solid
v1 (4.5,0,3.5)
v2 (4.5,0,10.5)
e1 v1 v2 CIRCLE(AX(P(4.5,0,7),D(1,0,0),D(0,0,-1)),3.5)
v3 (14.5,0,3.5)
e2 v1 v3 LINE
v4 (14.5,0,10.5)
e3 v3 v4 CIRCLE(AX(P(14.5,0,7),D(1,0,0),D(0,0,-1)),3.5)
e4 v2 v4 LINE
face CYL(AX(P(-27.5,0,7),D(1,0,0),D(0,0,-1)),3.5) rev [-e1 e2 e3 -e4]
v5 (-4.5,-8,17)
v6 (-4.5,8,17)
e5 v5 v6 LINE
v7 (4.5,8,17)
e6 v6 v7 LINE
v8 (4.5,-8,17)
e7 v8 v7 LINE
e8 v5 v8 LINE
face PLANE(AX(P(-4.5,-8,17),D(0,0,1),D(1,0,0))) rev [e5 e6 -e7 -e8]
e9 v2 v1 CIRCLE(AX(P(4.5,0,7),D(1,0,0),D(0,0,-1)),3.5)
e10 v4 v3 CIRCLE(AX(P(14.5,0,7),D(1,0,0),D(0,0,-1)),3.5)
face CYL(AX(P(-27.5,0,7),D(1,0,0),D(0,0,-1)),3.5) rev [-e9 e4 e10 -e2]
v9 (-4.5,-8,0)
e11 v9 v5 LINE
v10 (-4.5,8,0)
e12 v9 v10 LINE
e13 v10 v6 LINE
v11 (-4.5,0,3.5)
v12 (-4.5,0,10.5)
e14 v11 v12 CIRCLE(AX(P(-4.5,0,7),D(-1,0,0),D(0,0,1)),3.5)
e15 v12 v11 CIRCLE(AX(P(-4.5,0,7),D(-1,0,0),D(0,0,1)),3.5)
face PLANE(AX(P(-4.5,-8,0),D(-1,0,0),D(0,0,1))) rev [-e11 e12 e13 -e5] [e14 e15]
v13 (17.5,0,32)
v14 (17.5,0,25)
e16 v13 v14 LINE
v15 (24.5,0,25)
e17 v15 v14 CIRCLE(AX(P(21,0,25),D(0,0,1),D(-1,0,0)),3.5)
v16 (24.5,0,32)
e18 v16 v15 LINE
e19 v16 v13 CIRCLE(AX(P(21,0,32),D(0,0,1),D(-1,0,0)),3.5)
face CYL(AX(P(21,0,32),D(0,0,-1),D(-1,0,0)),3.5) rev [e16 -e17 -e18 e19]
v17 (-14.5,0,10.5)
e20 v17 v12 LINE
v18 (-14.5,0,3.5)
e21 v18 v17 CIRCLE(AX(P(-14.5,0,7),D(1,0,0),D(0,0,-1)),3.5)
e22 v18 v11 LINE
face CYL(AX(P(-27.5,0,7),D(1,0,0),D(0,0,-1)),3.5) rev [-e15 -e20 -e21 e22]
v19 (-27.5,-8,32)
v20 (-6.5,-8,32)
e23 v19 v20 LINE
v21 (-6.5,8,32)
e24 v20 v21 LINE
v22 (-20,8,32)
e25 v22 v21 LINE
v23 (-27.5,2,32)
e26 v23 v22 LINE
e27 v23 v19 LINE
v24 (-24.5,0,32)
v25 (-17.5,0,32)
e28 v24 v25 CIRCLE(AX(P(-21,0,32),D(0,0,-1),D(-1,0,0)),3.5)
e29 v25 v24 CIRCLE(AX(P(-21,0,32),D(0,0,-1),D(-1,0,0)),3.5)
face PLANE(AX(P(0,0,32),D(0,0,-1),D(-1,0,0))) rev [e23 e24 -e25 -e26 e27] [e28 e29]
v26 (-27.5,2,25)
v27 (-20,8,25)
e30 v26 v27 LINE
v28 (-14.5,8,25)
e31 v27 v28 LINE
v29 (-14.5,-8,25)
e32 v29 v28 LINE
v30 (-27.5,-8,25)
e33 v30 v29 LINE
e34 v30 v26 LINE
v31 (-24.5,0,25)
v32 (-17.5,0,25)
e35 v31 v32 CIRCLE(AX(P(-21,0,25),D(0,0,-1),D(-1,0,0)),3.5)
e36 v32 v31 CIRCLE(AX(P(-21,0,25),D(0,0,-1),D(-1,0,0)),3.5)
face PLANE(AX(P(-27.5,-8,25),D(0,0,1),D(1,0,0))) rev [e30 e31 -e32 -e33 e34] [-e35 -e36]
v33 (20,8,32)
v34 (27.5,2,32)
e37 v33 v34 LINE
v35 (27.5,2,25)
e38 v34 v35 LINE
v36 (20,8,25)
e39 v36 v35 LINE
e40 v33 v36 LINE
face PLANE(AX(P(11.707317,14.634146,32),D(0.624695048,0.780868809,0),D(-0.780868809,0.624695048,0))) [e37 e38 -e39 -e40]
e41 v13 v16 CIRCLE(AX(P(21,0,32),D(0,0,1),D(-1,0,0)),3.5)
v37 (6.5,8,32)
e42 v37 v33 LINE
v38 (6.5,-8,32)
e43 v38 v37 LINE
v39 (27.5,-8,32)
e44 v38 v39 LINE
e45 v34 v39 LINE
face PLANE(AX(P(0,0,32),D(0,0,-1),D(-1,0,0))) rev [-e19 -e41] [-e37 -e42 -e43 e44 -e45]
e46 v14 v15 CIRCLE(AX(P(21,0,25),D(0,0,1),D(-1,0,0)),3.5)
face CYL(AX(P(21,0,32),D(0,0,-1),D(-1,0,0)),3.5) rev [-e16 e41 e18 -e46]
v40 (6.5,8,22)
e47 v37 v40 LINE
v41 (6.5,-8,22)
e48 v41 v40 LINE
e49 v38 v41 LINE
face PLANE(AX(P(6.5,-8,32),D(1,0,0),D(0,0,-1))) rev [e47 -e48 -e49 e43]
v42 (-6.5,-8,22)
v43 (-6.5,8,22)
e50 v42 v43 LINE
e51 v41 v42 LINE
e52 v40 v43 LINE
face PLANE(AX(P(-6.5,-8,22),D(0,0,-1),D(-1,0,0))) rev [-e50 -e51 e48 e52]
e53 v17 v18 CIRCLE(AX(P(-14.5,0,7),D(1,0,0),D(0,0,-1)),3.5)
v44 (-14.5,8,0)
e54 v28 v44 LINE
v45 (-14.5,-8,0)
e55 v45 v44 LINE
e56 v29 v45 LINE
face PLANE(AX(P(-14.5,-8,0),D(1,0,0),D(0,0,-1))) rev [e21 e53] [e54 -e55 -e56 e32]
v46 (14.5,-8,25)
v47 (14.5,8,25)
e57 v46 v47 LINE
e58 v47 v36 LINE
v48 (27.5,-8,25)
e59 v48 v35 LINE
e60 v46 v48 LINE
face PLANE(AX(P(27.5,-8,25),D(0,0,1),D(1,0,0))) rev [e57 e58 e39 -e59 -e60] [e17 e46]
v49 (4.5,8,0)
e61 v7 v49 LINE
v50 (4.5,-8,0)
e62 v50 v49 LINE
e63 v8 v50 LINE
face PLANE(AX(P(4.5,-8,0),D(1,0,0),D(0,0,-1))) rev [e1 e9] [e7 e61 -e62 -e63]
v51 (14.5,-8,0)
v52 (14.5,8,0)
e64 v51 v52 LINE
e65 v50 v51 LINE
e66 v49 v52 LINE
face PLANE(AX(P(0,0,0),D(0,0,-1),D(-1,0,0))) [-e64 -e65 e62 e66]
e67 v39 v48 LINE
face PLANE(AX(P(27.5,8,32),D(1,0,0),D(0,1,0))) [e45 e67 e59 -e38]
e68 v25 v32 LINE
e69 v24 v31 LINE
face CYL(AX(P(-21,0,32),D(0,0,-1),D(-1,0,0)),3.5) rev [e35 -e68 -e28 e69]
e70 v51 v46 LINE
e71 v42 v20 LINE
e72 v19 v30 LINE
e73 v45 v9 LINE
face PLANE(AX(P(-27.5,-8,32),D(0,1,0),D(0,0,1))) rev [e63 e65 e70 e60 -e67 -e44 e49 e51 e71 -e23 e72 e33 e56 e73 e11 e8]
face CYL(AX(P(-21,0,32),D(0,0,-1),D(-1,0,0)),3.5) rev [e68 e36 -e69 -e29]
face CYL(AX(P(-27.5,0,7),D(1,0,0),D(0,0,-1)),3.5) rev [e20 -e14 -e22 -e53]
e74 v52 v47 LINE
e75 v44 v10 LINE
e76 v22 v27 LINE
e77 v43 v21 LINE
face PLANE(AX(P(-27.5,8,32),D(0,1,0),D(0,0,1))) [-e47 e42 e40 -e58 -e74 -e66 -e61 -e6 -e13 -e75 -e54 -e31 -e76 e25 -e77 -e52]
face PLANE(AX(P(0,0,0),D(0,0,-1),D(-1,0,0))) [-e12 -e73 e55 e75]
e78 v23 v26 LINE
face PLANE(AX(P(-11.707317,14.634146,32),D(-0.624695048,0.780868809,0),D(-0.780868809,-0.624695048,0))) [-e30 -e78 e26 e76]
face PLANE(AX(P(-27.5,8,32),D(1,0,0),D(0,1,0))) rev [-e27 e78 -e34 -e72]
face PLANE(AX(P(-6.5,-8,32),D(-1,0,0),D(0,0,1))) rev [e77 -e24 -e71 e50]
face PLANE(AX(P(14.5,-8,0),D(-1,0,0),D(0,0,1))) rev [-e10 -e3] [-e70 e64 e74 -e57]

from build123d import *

# Parameters (mm, degrees)
BASE_BLOCK_PROFILE_W        = 55
BASE_BLOCK_PROFILE_H        = 16
BASE_BLOCK_DEPTH            = 32
CENTRE_NOTCH_DEPTH          = 46.124826869
CENTRE_NOTCH_DEPTH_BACK     = 46.124826869
CENTRE_NOTCH_PROFILE_W      = 13
CENTRE_NOTCH_PROFILE_H      = 25
SIDE_STEP_CUT_DEPTH         = 46.124826869
SIDE_STEP_CUT_DEPTH_BACK    = 46.124826869
SIDE_STEP_CUT_PROFILE_W     = 13
SIDE_STEP_CUT_PROFILE_H     = 10
CORNER_BEVEL_CUT_DEPTH      = 46.124826869
CORNER_BEVEL_CUT_DEPTH_BACK = 46.124826869
CORNER_BEVEL_PROFILE_W      = 9
CORNER_BEVEL_PROFILE_H      = 17
LUG_SLOT_CUT_DEPTH          = 39.016443811
LUG_SLOT_CUT_DEPTH_BACK     = 39.016443811
LUG_HOLES_7_DEPTH           = 39.016443811
LUG_HOLES_7_DEPTH_BACK      = 39.016443811
LUG_HOLES_7_SKETCH_R        = 3.5
CROSS_HOLE_7_DEPTH          = 54.404119691
CROSS_HOLE_7_DEPTH_BACK     = 54.404119691
CROSS_HOLE_7_SKETCH_R       = 3.5


with BuildPart() as part:
    # Base Block Profile → Base Block (new body)
    with BuildSketch(Plane.XY):
        Rectangle(BASE_BLOCK_PROFILE_W, BASE_BLOCK_PROFILE_H)
    extrude(amount=BASE_BLOCK_DEPTH)

    # Centre Notch Profile → Centre Notch (cut, two sides: drawn at the far end of the back side and taken through both)
    with BuildSketch(Plane(origin=(0, 8, 0), x_dir=(1, 0, 0), z_dir=(0, 1, 0)).offset(-CENTRE_NOTCH_DEPTH_BACK)):
        with Locations((-21, -12.5)):
            Rectangle(CENTRE_NOTCH_PROFILE_W, CENTRE_NOTCH_PROFILE_H)
        with Locations((21, -12.5)):
            Rectangle(CENTRE_NOTCH_PROFILE_W, CENTRE_NOTCH_PROFILE_H)
    extrude(amount=CENTRE_NOTCH_DEPTH + CENTRE_NOTCH_DEPTH_BACK, mode=Mode.SUBTRACT)

    # Side Step Cut Profile → Side Step Cut (cut, two sides: drawn at the far end of the back side and taken through both)
    with BuildSketch(Plane(origin=(0, 8, 0), x_dir=(1, 0, 0), z_dir=(0, 1, 0)).offset(-SIDE_STEP_CUT_DEPTH_BACK)):
        with Locations((0, -27)):
            Rectangle(SIDE_STEP_CUT_PROFILE_W, SIDE_STEP_CUT_PROFILE_H)
    extrude(amount=SIDE_STEP_CUT_DEPTH + SIDE_STEP_CUT_DEPTH_BACK, mode=Mode.SUBTRACT)

    # Corner Bevel Profile → Corner Bevel Cut (cut, two sides: drawn at the far end of the back side and taken through both)
    with BuildSketch(Plane(origin=(0, 8, 0), x_dir=(1, 0, 0), z_dir=(0, 1, 0)).offset(-CORNER_BEVEL_CUT_DEPTH_BACK)):
        with Locations((0, -8.5)):
            Rectangle(CORNER_BEVEL_PROFILE_W, CORNER_BEVEL_PROFILE_H)
    extrude(amount=CORNER_BEVEL_CUT_DEPTH + CORNER_BEVEL_CUT_DEPTH_BACK, mode=Mode.SUBTRACT)

    # Lug Slot Profile → Lug Slot Cut (cut, two sides: drawn at the far end of the back side and taken through both)
    with BuildSketch(Plane(origin=(0, 0, 25), x_dir=(-1, 0, 0), z_dir=(0, 0, -1)).offset(-LUG_SLOT_CUT_DEPTH_BACK)):
        Polygon((-27.5, 8), (-20, 8), (-27.5, 2), align=None)
        Polygon((20, 8), (27.5, 2), (27.5, 8), align=None)
    extrude(amount=LUG_SLOT_CUT_DEPTH + LUG_SLOT_CUT_DEPTH_BACK, mode=Mode.SUBTRACT)

    # Lug Holes Ø7 Sketch → Lug Holes Ø7 (cut, two sides: drawn at the far end of the back side and taken through both)
    with BuildSketch(Plane(origin=(0, 0, 25), x_dir=(-1, 0, 0), z_dir=(0, 0, -1)).offset(-LUG_HOLES_7_DEPTH_BACK)):
        with BuildLine():
            ThreePointArc((24.5, 0), (21, 3.5), (17.5, 0))
            Line((17.5, 0), (24.5, 0))
        make_face()
        with BuildLine():
            Line((24.5, 0), (17.5, 0))
            ThreePointArc((17.5, 0), (21, -3.5), (24.5, 0))
        make_face()
        with Locations((-21, 0)):
            Circle(LUG_HOLES_7_SKETCH_R)
    extrude(amount=LUG_HOLES_7_DEPTH + LUG_HOLES_7_DEPTH_BACK, mode=Mode.SUBTRACT)

    # Cross Hole Ø7 Sketch → Cross Hole Ø7 (cut, two sides: drawn at the far end of the back side and taken through both)
    with BuildSketch(Plane(origin=(14.5, 0, 0), x_dir=(0, 0, -1), z_dir=(1, 0, 0)).offset(-CROSS_HOLE_7_DEPTH_BACK)):
        with Locations((-7, 0)):
            Circle(CROSS_HOLE_7_SKETCH_R)
    extrude(amount=CROSS_HOLE_7_DEPTH + CROSS_HOLE_7_DEPTH_BACK, mode=Mode.SUBTRACT)


solid = part.part
